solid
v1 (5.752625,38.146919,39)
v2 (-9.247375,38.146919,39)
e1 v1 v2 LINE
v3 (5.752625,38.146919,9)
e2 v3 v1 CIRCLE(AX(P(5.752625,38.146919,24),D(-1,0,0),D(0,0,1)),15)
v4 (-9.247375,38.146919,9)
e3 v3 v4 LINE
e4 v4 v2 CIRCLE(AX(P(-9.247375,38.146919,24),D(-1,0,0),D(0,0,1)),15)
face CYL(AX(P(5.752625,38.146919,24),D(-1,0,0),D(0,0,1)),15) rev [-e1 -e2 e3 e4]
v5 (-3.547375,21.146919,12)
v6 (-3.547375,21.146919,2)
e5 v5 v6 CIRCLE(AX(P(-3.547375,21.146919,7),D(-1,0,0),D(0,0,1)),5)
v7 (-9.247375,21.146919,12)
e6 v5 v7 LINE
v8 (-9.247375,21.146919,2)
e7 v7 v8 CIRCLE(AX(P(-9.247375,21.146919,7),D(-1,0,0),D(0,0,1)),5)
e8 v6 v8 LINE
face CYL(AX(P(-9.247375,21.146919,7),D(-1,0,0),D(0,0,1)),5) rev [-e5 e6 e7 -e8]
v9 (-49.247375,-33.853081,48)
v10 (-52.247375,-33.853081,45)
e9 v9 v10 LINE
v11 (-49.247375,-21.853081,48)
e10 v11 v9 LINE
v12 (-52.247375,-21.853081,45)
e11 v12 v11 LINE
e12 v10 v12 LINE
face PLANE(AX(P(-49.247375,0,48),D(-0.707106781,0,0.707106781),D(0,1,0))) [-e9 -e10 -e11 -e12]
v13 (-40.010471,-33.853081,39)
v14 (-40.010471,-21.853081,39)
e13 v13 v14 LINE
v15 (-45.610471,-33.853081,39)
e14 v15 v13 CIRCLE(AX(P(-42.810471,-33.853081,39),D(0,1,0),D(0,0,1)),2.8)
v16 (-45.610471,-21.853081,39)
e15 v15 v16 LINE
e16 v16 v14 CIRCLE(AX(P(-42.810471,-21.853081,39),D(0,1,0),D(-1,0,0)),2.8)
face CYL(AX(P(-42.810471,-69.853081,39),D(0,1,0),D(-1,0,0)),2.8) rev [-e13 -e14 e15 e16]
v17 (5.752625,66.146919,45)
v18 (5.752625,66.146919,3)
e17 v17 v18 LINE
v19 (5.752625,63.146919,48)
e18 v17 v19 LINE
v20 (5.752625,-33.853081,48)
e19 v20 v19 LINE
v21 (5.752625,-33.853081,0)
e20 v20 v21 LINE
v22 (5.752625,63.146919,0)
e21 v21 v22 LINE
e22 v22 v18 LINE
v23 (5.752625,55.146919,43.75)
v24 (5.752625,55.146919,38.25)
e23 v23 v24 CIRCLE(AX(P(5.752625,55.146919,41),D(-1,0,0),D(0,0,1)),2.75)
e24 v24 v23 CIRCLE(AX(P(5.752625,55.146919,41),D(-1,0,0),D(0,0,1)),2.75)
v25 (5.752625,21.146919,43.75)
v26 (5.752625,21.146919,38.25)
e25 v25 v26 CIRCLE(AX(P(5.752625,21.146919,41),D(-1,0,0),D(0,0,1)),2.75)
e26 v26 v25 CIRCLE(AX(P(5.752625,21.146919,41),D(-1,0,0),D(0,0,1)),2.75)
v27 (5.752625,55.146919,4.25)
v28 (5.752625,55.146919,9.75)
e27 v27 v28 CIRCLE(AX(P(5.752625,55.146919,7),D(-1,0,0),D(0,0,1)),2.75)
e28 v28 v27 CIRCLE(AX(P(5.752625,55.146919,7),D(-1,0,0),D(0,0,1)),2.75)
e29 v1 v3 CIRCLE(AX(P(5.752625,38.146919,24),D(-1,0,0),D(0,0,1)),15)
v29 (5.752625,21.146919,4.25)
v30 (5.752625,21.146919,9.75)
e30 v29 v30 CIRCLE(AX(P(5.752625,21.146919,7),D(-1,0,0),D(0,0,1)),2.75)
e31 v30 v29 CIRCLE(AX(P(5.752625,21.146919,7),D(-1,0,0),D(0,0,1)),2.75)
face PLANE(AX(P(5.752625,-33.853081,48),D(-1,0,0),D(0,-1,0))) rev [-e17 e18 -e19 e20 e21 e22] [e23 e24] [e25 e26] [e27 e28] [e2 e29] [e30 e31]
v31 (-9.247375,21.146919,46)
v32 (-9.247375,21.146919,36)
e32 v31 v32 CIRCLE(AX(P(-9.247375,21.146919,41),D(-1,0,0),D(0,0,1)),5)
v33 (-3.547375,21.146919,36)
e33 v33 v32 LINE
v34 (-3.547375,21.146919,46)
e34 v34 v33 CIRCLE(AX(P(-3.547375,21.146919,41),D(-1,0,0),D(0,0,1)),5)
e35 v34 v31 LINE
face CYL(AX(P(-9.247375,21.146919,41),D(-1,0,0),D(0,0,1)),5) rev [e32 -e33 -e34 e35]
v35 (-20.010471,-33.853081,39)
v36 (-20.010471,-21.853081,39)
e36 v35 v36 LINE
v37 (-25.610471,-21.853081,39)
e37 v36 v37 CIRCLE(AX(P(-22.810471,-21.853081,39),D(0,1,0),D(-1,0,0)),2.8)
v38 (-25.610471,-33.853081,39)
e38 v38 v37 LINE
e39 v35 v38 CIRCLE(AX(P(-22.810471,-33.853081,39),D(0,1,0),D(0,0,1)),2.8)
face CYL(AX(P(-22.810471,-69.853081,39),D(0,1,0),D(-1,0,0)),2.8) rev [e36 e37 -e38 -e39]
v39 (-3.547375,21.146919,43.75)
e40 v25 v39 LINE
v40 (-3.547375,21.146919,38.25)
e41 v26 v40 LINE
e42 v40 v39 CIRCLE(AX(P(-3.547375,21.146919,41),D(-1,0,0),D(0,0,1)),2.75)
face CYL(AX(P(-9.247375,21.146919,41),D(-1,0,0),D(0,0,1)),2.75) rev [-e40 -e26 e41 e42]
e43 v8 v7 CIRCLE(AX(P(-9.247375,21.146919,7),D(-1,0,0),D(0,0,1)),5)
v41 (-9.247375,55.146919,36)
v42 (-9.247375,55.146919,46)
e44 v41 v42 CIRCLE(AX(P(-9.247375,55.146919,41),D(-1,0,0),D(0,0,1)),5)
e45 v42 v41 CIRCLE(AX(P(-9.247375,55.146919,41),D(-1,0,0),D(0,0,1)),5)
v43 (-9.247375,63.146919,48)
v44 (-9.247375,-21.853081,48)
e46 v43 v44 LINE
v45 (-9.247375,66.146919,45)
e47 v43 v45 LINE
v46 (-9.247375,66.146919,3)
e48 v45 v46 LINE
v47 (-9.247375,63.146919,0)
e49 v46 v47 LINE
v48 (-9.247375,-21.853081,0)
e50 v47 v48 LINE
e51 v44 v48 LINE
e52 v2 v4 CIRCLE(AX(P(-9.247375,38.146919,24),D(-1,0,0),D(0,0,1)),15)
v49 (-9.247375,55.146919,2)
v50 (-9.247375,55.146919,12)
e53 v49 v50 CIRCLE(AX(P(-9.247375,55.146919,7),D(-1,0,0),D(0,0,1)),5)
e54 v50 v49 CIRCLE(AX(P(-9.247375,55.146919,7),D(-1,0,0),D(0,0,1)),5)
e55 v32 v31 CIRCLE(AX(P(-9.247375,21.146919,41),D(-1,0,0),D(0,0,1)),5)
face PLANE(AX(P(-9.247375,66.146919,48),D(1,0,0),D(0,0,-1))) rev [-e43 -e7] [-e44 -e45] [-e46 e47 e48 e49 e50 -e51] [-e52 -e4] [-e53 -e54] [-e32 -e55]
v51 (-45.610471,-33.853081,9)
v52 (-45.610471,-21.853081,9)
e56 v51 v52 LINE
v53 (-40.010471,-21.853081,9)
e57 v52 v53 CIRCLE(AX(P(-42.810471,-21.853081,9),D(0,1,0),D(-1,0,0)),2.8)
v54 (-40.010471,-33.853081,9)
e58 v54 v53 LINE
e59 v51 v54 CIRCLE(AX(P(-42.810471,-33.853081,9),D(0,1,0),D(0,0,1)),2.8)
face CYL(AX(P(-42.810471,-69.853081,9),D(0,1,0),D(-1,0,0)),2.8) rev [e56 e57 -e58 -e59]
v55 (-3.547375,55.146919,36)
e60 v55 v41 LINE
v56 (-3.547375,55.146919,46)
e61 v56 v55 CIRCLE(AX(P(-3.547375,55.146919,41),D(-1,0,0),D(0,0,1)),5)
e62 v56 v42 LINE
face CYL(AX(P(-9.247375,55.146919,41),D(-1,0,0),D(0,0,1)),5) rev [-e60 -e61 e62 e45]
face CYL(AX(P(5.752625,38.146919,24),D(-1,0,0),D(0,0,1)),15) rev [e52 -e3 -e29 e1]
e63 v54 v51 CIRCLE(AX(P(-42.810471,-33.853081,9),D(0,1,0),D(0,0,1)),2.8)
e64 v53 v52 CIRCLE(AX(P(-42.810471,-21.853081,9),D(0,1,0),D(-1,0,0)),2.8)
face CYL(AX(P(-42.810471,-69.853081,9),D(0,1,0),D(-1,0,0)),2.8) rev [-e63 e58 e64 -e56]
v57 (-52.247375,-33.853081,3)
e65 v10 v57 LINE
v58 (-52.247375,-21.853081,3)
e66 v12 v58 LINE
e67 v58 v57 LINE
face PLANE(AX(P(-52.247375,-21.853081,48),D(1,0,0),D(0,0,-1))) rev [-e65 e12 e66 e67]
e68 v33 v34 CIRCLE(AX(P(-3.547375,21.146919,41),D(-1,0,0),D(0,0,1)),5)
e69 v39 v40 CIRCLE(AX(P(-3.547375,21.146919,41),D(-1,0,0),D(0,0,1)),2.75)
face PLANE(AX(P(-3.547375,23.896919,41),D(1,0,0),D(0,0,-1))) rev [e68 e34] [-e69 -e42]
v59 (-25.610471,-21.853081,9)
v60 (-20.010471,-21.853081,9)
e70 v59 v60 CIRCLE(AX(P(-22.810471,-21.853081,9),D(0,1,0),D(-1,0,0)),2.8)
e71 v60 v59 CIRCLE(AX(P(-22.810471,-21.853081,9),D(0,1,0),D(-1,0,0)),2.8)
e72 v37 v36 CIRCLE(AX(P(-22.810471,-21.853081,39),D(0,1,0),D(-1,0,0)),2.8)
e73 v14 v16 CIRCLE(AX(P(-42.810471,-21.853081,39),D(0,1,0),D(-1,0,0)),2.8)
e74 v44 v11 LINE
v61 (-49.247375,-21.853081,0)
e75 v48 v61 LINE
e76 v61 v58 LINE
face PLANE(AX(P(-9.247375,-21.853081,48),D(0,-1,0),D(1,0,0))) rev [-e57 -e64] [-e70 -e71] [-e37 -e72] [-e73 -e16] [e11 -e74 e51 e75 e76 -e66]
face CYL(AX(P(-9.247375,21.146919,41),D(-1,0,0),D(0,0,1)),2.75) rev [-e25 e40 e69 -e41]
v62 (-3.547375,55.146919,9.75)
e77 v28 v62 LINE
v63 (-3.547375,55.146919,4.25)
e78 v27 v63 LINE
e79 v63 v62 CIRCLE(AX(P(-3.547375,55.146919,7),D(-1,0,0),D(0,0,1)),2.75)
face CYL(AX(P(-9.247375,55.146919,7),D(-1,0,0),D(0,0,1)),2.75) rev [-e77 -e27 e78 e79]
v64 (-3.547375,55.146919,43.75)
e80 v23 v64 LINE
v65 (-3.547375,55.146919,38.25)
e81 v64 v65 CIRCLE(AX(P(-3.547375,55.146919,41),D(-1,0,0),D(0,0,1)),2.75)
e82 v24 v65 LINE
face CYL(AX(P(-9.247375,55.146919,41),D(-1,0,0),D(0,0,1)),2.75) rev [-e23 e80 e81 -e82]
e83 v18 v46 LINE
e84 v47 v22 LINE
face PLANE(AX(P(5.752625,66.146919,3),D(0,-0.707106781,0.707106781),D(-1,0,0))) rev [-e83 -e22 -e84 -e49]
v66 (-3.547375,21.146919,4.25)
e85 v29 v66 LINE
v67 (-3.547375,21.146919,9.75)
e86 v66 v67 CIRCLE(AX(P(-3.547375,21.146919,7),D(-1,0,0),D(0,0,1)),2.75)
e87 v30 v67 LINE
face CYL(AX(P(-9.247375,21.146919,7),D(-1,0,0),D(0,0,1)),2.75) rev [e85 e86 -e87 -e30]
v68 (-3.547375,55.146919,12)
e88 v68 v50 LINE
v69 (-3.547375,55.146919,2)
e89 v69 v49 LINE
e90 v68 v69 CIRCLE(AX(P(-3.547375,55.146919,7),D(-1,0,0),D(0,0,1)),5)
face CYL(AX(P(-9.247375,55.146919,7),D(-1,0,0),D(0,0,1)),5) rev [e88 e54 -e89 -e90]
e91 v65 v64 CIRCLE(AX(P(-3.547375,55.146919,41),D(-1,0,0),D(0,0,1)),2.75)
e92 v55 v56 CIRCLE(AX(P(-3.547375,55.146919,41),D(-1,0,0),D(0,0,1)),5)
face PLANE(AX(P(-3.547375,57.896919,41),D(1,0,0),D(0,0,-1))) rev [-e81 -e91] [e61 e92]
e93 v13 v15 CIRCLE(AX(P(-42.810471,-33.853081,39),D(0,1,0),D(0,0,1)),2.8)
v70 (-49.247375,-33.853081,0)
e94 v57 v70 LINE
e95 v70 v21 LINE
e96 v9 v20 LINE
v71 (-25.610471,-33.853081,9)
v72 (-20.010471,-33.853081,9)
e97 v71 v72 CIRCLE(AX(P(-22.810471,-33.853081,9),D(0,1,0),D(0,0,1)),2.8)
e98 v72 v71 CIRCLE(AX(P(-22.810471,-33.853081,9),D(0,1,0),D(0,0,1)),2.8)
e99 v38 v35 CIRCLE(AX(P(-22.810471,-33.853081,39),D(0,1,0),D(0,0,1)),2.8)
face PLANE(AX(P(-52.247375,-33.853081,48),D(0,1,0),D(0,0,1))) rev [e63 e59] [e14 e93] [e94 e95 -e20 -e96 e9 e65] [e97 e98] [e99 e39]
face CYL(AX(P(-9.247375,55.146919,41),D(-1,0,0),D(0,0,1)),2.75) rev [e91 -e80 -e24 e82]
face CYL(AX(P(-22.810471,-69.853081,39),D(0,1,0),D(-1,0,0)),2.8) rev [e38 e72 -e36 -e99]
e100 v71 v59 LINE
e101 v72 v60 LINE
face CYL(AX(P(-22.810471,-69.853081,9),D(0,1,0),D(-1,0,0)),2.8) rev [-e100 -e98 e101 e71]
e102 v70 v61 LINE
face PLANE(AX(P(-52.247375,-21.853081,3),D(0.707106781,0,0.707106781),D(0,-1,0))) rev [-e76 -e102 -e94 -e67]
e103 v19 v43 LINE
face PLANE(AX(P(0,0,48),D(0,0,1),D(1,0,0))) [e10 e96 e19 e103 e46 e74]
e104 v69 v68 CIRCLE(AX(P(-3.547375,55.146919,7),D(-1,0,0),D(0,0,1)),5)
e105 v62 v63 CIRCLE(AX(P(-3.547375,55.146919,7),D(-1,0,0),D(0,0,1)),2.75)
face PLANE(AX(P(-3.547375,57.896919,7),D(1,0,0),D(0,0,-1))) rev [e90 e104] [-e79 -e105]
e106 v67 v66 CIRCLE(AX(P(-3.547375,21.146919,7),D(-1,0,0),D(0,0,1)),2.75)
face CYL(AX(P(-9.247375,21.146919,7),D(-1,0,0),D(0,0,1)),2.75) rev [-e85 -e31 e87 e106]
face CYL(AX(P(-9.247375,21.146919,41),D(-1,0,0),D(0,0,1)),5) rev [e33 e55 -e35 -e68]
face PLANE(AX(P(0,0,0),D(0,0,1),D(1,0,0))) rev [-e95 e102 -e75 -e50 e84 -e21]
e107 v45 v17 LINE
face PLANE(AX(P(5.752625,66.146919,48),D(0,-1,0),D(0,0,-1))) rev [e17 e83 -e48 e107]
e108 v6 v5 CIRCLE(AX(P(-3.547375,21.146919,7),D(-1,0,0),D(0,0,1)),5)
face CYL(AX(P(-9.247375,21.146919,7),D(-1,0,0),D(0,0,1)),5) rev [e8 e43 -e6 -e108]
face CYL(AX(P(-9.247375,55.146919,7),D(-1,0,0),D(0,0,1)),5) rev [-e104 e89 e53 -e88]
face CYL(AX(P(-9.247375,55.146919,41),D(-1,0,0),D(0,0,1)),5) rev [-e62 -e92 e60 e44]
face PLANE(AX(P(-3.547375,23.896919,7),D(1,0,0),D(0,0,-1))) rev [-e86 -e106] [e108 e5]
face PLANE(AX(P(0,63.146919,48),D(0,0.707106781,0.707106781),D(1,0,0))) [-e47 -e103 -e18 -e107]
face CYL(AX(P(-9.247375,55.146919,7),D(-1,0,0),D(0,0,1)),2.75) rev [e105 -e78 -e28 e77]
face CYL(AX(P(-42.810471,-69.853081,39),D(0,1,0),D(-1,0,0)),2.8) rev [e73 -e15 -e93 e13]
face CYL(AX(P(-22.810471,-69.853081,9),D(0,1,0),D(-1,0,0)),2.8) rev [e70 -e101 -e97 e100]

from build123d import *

# Parameters (mm, degrees)
BOSS_EXTRUDE1_DEPTH                                = 48
SKETCH2_R                                          = 15
CUT_EXTRUDE1_DEPTH                                 = 93.349417704
HOLE_SIZE_PER_HEX_SOCKET_CAP_SCREW_TYP_D           = 5.5
HOLE_SIZE_PER_HEX_SOCKET_CAP_SCREW_TYP_CBORE_D     = 10
HOLE_SIZE_PER_HEX_SOCKET_CAP_SCREW_TYP_CBORE_DEPTH = 5.7
CHAMFER1_SIZE                                      = 3
SKETCH6_R                                          = 2.8
CUT_EXTRUDE2_DEPTH                                 = 48


with BuildPart() as part:
    # Sketch1 → Boss-Extrude1 (new body)
    with BuildSketch(Plane.XY):
        Polygon((-9.247374932, 66.146919431), (-9.247374932, -21.853080569), (-52.247374932, -21.853080569), (-52.247374932, -33.853080569), (5.752625068, -33.853080569), (5.752625068, 66.146919431), align=None)
    extrude(amount=BOSS_EXTRUDE1_DEPTH)

    # Sketch2 → Cut-Extrude1 (cut, through all)
    with BuildSketch(Plane.ZY.offset(9.247374932)):
        with Locations((24, 38.146919431)):
            Circle(SKETCH2_R)
    extrude(amount=-CUT_EXTRUDE1_DEPTH, mode=Mode.SUBTRACT)

    # Hole size (per) hex socket cap screw type 1 (through all)
    with Locations(Plane.ZY.offset(9.247374932)):
        with Locations((7, 55.146919431), (41, 55.146919431), (41, 21.146919431), (7, 21.146919431)):
            CounterBoreHole(HOLE_SIZE_PER_HEX_SOCKET_CAP_SCREW_TYP_D / 2, HOLE_SIZE_PER_HEX_SOCKET_CAP_SCREW_TYP_CBORE_D / 2, HOLE_SIZE_PER_HEX_SOCKET_CAP_SCREW_TYP_CBORE_DEPTH)

    # Chamfer1
    chamfer1_edges = [part.edges().sort_by_distance(p)[0] for p in [
        (-52.247374932, -27.853080569, 48),
        (-1.747374932, 66.146919431, 48),
        (-52.247374932, -27.853080569, 0),
        (-1.747374932, 66.146919431, 0),
    ]]
    chamfer(chamfer1_edges, length=CHAMFER1_SIZE)

    # Sketch6 → Cut-Extrude2 (cut)
    with BuildSketch(Plane(origin=(0, -21.853080569, 0), x_dir=(1, 0, 0), z_dir=(0, 1, 0))):
        with Locations(Location((-42.810470963, -9, 0), (0, 0, 180))):
            Circle(SKETCH6_R)
        with Locations(Location((-22.810470963, -9, 0), (0, 0, 180))):
            Circle(SKETCH6_R)
        with Locations(Location((-42.810470963, -39, 0), (0, 0, 180))):
            Circle(SKETCH6_R)
        with Locations(Location((-22.810470963, -39, 0), (0, 0, 180))):
            Circle(SKETCH6_R)
    extrude(amount=-CUT_EXTRUDE2_DEPTH, mode=Mode.SUBTRACT)


solid = part.part
